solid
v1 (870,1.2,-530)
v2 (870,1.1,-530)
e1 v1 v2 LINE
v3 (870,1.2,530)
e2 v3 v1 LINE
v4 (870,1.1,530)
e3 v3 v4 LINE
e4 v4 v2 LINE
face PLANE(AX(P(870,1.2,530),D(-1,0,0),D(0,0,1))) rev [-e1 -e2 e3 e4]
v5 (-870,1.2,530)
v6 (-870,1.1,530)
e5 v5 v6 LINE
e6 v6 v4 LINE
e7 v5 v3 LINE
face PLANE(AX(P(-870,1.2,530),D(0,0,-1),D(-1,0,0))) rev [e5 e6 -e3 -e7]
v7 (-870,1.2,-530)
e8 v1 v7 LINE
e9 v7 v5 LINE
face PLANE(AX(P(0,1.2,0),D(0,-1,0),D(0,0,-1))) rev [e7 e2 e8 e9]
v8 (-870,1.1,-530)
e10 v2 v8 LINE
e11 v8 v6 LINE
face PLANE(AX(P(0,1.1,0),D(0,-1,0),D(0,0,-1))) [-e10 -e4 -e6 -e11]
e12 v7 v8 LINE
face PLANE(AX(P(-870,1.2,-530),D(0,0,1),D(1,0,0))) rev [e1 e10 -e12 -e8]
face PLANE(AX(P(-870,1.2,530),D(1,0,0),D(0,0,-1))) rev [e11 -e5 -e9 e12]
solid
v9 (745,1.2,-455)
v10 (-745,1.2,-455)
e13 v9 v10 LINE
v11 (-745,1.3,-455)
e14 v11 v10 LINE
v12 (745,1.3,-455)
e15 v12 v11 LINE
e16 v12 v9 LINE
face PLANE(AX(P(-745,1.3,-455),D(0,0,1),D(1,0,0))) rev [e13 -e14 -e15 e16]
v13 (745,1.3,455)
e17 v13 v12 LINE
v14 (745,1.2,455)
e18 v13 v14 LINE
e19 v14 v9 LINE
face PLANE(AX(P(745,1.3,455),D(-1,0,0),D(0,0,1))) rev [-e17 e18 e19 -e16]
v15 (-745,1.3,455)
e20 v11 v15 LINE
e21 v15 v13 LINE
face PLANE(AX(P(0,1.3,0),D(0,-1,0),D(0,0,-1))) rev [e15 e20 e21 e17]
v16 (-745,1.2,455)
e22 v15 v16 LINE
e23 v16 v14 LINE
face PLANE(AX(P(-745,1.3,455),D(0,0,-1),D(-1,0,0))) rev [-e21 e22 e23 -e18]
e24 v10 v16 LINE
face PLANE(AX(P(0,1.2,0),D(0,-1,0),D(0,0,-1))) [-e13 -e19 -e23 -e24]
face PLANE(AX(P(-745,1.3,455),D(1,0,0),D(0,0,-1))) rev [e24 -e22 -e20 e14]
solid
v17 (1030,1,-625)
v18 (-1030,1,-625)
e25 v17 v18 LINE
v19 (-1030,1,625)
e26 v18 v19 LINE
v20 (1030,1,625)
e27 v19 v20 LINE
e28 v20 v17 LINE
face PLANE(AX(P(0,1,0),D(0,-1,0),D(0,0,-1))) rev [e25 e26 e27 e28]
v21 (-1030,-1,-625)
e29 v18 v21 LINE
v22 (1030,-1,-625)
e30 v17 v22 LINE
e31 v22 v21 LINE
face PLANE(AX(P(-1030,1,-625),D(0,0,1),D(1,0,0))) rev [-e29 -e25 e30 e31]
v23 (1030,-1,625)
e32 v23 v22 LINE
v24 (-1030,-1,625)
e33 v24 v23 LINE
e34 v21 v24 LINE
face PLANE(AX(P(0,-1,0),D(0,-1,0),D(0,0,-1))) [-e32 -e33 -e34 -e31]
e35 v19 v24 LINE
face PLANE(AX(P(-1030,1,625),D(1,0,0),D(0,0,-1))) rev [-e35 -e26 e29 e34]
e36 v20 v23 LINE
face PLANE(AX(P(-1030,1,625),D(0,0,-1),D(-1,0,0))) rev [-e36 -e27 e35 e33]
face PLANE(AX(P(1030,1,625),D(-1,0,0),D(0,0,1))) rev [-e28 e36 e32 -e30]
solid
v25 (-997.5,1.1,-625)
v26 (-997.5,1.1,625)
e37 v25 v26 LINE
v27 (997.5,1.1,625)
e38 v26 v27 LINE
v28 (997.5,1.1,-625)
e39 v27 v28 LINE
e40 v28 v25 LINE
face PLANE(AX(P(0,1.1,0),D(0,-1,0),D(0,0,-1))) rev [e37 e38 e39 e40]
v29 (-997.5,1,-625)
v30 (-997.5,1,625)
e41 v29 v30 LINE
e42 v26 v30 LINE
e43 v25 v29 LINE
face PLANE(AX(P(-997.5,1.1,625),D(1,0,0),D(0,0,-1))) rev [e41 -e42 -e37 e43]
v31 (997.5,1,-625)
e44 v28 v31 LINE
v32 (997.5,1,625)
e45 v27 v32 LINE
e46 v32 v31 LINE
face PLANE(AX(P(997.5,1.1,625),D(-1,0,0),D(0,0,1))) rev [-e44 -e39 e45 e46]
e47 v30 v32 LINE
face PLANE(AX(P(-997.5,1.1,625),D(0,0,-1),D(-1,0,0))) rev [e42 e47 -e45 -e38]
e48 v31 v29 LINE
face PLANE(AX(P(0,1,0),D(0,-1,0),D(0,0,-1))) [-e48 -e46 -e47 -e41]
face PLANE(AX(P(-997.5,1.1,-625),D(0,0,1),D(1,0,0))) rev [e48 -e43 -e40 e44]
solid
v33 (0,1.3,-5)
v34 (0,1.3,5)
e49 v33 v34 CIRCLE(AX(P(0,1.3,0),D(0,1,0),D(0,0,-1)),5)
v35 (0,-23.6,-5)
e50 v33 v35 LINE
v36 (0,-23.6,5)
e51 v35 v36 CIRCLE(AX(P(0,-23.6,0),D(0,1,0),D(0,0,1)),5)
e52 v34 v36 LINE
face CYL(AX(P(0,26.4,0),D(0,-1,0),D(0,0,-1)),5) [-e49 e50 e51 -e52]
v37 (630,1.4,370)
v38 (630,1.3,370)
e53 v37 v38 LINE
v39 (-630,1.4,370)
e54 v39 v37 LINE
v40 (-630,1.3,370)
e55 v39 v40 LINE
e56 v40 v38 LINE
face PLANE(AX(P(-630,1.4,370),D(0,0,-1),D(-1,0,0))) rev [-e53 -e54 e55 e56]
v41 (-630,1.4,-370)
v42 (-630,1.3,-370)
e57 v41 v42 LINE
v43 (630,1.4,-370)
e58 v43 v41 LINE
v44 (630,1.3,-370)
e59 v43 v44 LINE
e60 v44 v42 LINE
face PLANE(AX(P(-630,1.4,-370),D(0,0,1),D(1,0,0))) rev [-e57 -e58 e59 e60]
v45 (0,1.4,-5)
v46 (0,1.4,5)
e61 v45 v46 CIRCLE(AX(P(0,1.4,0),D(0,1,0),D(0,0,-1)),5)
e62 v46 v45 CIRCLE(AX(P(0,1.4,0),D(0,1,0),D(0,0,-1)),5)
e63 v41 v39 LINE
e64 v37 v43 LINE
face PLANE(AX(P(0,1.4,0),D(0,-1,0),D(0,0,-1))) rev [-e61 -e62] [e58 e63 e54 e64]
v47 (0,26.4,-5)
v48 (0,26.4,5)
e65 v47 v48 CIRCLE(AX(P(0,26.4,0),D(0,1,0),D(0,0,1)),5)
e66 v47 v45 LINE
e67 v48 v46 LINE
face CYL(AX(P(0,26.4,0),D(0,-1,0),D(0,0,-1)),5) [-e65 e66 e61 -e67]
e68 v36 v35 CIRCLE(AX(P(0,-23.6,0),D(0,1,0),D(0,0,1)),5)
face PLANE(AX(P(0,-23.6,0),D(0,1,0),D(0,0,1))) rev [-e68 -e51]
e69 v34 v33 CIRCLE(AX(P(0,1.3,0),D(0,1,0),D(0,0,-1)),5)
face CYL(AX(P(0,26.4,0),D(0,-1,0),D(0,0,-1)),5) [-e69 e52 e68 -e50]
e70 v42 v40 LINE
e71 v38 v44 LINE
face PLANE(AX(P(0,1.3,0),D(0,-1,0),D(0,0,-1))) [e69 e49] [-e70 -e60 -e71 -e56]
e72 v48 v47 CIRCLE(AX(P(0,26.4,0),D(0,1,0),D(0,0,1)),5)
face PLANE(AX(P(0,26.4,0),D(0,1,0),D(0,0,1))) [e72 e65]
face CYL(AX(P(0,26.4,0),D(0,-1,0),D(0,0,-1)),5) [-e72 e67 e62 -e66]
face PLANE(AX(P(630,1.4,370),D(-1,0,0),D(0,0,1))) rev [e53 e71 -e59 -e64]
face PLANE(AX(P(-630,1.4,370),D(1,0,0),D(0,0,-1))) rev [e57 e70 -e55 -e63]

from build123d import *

# Parameters (mm, degrees)
SKETCH_1_W      = 2060
SKETCH_1_H      = 1250
EXTRUDE_1_DEPTH = 1
SKETCH_2_W      = 1995
SKETCH_2_H      = 1250
EXTRUDE_2_DEPTH = 0.1
SKETCH_3_W      = 1740
SKETCH_3_H      = 1060
EXTRUDE_5_DEPTH = 0.1
SKETCH_4_W      = 1490
SKETCH_4_H      = 910
EXTRUDE_6_DEPTH = 0.1
SKETCH_5_W      = 1260
SKETCH_5_H      = 740
EXTRUDE_7_DEPTH = 0.1
SKETCH_6_R      = 5
EXTRUDE_8_DEPTH = 25


with BuildPart() as part:
    # 草图1 → 凸台-拉伸1 (new, symmetric)
    with BuildSketch(Plane(origin=(0, 0, 0), x_dir=(1, 0, 0), z_dir=(0, 1, 0))):
        Rectangle(SKETCH_1_W, SKETCH_1_H)
    extrude(amount=EXTRUDE_1_DEPTH, both=True)


with BuildPart() as body_2:
    # 草图2 → 凸台-拉伸2 (new body)
    with BuildSketch(Plane(origin=(0, 1, 0), x_dir=(1, 0, 0), z_dir=(0, 1, 0))):
        Rectangle(SKETCH_2_W, SKETCH_2_H)
    extrude(amount=EXTRUDE_2_DEPTH)


with BuildPart() as body_3:
    # 草图3 → 凸台-拉伸5 (new body)
    with BuildSketch(Plane(origin=(0, 1.1, 0), x_dir=(1, 0, 0), z_dir=(0, 1, 0))):
        Rectangle(SKETCH_3_W, SKETCH_3_H)
    extrude(amount=EXTRUDE_5_DEPTH)


with BuildPart() as body_4:
    # 草图4 → 凸台-拉伸6 (new body)
    with BuildSketch(Plane(origin=(0, 1.2, 0), x_dir=(1, 0, 0), z_dir=(0, 1, 0))):
        Rectangle(SKETCH_4_W, SKETCH_4_H)
    extrude(amount=EXTRUDE_6_DEPTH)


with BuildPart() as body_5:
    # 草图5 → 凸台-拉伸7 (new body)
    with BuildSketch(Plane(origin=(0, 1.3, 0), x_dir=(1, 0, 0), z_dir=(0, 1, 0))):
        Rectangle(SKETCH_5_W, SKETCH_5_H)
    extrude(amount=EXTRUDE_7_DEPTH)

    # 草图6 → 凸台-拉伸8 (add, symmetric)
    with BuildSketch(Plane(origin=(0, 1.4, 0), x_dir=(1, 0, 0), z_dir=(0, 1, 0))):
        with Locations(Location((0, 0, 0), (0, 0, 90))):
            Circle(SKETCH_6_R)
    extrude(amount=EXTRUDE_8_DEPTH, both=True)


solid = Compound([part.part, body_2.part, body_3.part, body_4.part, body_5.part])
